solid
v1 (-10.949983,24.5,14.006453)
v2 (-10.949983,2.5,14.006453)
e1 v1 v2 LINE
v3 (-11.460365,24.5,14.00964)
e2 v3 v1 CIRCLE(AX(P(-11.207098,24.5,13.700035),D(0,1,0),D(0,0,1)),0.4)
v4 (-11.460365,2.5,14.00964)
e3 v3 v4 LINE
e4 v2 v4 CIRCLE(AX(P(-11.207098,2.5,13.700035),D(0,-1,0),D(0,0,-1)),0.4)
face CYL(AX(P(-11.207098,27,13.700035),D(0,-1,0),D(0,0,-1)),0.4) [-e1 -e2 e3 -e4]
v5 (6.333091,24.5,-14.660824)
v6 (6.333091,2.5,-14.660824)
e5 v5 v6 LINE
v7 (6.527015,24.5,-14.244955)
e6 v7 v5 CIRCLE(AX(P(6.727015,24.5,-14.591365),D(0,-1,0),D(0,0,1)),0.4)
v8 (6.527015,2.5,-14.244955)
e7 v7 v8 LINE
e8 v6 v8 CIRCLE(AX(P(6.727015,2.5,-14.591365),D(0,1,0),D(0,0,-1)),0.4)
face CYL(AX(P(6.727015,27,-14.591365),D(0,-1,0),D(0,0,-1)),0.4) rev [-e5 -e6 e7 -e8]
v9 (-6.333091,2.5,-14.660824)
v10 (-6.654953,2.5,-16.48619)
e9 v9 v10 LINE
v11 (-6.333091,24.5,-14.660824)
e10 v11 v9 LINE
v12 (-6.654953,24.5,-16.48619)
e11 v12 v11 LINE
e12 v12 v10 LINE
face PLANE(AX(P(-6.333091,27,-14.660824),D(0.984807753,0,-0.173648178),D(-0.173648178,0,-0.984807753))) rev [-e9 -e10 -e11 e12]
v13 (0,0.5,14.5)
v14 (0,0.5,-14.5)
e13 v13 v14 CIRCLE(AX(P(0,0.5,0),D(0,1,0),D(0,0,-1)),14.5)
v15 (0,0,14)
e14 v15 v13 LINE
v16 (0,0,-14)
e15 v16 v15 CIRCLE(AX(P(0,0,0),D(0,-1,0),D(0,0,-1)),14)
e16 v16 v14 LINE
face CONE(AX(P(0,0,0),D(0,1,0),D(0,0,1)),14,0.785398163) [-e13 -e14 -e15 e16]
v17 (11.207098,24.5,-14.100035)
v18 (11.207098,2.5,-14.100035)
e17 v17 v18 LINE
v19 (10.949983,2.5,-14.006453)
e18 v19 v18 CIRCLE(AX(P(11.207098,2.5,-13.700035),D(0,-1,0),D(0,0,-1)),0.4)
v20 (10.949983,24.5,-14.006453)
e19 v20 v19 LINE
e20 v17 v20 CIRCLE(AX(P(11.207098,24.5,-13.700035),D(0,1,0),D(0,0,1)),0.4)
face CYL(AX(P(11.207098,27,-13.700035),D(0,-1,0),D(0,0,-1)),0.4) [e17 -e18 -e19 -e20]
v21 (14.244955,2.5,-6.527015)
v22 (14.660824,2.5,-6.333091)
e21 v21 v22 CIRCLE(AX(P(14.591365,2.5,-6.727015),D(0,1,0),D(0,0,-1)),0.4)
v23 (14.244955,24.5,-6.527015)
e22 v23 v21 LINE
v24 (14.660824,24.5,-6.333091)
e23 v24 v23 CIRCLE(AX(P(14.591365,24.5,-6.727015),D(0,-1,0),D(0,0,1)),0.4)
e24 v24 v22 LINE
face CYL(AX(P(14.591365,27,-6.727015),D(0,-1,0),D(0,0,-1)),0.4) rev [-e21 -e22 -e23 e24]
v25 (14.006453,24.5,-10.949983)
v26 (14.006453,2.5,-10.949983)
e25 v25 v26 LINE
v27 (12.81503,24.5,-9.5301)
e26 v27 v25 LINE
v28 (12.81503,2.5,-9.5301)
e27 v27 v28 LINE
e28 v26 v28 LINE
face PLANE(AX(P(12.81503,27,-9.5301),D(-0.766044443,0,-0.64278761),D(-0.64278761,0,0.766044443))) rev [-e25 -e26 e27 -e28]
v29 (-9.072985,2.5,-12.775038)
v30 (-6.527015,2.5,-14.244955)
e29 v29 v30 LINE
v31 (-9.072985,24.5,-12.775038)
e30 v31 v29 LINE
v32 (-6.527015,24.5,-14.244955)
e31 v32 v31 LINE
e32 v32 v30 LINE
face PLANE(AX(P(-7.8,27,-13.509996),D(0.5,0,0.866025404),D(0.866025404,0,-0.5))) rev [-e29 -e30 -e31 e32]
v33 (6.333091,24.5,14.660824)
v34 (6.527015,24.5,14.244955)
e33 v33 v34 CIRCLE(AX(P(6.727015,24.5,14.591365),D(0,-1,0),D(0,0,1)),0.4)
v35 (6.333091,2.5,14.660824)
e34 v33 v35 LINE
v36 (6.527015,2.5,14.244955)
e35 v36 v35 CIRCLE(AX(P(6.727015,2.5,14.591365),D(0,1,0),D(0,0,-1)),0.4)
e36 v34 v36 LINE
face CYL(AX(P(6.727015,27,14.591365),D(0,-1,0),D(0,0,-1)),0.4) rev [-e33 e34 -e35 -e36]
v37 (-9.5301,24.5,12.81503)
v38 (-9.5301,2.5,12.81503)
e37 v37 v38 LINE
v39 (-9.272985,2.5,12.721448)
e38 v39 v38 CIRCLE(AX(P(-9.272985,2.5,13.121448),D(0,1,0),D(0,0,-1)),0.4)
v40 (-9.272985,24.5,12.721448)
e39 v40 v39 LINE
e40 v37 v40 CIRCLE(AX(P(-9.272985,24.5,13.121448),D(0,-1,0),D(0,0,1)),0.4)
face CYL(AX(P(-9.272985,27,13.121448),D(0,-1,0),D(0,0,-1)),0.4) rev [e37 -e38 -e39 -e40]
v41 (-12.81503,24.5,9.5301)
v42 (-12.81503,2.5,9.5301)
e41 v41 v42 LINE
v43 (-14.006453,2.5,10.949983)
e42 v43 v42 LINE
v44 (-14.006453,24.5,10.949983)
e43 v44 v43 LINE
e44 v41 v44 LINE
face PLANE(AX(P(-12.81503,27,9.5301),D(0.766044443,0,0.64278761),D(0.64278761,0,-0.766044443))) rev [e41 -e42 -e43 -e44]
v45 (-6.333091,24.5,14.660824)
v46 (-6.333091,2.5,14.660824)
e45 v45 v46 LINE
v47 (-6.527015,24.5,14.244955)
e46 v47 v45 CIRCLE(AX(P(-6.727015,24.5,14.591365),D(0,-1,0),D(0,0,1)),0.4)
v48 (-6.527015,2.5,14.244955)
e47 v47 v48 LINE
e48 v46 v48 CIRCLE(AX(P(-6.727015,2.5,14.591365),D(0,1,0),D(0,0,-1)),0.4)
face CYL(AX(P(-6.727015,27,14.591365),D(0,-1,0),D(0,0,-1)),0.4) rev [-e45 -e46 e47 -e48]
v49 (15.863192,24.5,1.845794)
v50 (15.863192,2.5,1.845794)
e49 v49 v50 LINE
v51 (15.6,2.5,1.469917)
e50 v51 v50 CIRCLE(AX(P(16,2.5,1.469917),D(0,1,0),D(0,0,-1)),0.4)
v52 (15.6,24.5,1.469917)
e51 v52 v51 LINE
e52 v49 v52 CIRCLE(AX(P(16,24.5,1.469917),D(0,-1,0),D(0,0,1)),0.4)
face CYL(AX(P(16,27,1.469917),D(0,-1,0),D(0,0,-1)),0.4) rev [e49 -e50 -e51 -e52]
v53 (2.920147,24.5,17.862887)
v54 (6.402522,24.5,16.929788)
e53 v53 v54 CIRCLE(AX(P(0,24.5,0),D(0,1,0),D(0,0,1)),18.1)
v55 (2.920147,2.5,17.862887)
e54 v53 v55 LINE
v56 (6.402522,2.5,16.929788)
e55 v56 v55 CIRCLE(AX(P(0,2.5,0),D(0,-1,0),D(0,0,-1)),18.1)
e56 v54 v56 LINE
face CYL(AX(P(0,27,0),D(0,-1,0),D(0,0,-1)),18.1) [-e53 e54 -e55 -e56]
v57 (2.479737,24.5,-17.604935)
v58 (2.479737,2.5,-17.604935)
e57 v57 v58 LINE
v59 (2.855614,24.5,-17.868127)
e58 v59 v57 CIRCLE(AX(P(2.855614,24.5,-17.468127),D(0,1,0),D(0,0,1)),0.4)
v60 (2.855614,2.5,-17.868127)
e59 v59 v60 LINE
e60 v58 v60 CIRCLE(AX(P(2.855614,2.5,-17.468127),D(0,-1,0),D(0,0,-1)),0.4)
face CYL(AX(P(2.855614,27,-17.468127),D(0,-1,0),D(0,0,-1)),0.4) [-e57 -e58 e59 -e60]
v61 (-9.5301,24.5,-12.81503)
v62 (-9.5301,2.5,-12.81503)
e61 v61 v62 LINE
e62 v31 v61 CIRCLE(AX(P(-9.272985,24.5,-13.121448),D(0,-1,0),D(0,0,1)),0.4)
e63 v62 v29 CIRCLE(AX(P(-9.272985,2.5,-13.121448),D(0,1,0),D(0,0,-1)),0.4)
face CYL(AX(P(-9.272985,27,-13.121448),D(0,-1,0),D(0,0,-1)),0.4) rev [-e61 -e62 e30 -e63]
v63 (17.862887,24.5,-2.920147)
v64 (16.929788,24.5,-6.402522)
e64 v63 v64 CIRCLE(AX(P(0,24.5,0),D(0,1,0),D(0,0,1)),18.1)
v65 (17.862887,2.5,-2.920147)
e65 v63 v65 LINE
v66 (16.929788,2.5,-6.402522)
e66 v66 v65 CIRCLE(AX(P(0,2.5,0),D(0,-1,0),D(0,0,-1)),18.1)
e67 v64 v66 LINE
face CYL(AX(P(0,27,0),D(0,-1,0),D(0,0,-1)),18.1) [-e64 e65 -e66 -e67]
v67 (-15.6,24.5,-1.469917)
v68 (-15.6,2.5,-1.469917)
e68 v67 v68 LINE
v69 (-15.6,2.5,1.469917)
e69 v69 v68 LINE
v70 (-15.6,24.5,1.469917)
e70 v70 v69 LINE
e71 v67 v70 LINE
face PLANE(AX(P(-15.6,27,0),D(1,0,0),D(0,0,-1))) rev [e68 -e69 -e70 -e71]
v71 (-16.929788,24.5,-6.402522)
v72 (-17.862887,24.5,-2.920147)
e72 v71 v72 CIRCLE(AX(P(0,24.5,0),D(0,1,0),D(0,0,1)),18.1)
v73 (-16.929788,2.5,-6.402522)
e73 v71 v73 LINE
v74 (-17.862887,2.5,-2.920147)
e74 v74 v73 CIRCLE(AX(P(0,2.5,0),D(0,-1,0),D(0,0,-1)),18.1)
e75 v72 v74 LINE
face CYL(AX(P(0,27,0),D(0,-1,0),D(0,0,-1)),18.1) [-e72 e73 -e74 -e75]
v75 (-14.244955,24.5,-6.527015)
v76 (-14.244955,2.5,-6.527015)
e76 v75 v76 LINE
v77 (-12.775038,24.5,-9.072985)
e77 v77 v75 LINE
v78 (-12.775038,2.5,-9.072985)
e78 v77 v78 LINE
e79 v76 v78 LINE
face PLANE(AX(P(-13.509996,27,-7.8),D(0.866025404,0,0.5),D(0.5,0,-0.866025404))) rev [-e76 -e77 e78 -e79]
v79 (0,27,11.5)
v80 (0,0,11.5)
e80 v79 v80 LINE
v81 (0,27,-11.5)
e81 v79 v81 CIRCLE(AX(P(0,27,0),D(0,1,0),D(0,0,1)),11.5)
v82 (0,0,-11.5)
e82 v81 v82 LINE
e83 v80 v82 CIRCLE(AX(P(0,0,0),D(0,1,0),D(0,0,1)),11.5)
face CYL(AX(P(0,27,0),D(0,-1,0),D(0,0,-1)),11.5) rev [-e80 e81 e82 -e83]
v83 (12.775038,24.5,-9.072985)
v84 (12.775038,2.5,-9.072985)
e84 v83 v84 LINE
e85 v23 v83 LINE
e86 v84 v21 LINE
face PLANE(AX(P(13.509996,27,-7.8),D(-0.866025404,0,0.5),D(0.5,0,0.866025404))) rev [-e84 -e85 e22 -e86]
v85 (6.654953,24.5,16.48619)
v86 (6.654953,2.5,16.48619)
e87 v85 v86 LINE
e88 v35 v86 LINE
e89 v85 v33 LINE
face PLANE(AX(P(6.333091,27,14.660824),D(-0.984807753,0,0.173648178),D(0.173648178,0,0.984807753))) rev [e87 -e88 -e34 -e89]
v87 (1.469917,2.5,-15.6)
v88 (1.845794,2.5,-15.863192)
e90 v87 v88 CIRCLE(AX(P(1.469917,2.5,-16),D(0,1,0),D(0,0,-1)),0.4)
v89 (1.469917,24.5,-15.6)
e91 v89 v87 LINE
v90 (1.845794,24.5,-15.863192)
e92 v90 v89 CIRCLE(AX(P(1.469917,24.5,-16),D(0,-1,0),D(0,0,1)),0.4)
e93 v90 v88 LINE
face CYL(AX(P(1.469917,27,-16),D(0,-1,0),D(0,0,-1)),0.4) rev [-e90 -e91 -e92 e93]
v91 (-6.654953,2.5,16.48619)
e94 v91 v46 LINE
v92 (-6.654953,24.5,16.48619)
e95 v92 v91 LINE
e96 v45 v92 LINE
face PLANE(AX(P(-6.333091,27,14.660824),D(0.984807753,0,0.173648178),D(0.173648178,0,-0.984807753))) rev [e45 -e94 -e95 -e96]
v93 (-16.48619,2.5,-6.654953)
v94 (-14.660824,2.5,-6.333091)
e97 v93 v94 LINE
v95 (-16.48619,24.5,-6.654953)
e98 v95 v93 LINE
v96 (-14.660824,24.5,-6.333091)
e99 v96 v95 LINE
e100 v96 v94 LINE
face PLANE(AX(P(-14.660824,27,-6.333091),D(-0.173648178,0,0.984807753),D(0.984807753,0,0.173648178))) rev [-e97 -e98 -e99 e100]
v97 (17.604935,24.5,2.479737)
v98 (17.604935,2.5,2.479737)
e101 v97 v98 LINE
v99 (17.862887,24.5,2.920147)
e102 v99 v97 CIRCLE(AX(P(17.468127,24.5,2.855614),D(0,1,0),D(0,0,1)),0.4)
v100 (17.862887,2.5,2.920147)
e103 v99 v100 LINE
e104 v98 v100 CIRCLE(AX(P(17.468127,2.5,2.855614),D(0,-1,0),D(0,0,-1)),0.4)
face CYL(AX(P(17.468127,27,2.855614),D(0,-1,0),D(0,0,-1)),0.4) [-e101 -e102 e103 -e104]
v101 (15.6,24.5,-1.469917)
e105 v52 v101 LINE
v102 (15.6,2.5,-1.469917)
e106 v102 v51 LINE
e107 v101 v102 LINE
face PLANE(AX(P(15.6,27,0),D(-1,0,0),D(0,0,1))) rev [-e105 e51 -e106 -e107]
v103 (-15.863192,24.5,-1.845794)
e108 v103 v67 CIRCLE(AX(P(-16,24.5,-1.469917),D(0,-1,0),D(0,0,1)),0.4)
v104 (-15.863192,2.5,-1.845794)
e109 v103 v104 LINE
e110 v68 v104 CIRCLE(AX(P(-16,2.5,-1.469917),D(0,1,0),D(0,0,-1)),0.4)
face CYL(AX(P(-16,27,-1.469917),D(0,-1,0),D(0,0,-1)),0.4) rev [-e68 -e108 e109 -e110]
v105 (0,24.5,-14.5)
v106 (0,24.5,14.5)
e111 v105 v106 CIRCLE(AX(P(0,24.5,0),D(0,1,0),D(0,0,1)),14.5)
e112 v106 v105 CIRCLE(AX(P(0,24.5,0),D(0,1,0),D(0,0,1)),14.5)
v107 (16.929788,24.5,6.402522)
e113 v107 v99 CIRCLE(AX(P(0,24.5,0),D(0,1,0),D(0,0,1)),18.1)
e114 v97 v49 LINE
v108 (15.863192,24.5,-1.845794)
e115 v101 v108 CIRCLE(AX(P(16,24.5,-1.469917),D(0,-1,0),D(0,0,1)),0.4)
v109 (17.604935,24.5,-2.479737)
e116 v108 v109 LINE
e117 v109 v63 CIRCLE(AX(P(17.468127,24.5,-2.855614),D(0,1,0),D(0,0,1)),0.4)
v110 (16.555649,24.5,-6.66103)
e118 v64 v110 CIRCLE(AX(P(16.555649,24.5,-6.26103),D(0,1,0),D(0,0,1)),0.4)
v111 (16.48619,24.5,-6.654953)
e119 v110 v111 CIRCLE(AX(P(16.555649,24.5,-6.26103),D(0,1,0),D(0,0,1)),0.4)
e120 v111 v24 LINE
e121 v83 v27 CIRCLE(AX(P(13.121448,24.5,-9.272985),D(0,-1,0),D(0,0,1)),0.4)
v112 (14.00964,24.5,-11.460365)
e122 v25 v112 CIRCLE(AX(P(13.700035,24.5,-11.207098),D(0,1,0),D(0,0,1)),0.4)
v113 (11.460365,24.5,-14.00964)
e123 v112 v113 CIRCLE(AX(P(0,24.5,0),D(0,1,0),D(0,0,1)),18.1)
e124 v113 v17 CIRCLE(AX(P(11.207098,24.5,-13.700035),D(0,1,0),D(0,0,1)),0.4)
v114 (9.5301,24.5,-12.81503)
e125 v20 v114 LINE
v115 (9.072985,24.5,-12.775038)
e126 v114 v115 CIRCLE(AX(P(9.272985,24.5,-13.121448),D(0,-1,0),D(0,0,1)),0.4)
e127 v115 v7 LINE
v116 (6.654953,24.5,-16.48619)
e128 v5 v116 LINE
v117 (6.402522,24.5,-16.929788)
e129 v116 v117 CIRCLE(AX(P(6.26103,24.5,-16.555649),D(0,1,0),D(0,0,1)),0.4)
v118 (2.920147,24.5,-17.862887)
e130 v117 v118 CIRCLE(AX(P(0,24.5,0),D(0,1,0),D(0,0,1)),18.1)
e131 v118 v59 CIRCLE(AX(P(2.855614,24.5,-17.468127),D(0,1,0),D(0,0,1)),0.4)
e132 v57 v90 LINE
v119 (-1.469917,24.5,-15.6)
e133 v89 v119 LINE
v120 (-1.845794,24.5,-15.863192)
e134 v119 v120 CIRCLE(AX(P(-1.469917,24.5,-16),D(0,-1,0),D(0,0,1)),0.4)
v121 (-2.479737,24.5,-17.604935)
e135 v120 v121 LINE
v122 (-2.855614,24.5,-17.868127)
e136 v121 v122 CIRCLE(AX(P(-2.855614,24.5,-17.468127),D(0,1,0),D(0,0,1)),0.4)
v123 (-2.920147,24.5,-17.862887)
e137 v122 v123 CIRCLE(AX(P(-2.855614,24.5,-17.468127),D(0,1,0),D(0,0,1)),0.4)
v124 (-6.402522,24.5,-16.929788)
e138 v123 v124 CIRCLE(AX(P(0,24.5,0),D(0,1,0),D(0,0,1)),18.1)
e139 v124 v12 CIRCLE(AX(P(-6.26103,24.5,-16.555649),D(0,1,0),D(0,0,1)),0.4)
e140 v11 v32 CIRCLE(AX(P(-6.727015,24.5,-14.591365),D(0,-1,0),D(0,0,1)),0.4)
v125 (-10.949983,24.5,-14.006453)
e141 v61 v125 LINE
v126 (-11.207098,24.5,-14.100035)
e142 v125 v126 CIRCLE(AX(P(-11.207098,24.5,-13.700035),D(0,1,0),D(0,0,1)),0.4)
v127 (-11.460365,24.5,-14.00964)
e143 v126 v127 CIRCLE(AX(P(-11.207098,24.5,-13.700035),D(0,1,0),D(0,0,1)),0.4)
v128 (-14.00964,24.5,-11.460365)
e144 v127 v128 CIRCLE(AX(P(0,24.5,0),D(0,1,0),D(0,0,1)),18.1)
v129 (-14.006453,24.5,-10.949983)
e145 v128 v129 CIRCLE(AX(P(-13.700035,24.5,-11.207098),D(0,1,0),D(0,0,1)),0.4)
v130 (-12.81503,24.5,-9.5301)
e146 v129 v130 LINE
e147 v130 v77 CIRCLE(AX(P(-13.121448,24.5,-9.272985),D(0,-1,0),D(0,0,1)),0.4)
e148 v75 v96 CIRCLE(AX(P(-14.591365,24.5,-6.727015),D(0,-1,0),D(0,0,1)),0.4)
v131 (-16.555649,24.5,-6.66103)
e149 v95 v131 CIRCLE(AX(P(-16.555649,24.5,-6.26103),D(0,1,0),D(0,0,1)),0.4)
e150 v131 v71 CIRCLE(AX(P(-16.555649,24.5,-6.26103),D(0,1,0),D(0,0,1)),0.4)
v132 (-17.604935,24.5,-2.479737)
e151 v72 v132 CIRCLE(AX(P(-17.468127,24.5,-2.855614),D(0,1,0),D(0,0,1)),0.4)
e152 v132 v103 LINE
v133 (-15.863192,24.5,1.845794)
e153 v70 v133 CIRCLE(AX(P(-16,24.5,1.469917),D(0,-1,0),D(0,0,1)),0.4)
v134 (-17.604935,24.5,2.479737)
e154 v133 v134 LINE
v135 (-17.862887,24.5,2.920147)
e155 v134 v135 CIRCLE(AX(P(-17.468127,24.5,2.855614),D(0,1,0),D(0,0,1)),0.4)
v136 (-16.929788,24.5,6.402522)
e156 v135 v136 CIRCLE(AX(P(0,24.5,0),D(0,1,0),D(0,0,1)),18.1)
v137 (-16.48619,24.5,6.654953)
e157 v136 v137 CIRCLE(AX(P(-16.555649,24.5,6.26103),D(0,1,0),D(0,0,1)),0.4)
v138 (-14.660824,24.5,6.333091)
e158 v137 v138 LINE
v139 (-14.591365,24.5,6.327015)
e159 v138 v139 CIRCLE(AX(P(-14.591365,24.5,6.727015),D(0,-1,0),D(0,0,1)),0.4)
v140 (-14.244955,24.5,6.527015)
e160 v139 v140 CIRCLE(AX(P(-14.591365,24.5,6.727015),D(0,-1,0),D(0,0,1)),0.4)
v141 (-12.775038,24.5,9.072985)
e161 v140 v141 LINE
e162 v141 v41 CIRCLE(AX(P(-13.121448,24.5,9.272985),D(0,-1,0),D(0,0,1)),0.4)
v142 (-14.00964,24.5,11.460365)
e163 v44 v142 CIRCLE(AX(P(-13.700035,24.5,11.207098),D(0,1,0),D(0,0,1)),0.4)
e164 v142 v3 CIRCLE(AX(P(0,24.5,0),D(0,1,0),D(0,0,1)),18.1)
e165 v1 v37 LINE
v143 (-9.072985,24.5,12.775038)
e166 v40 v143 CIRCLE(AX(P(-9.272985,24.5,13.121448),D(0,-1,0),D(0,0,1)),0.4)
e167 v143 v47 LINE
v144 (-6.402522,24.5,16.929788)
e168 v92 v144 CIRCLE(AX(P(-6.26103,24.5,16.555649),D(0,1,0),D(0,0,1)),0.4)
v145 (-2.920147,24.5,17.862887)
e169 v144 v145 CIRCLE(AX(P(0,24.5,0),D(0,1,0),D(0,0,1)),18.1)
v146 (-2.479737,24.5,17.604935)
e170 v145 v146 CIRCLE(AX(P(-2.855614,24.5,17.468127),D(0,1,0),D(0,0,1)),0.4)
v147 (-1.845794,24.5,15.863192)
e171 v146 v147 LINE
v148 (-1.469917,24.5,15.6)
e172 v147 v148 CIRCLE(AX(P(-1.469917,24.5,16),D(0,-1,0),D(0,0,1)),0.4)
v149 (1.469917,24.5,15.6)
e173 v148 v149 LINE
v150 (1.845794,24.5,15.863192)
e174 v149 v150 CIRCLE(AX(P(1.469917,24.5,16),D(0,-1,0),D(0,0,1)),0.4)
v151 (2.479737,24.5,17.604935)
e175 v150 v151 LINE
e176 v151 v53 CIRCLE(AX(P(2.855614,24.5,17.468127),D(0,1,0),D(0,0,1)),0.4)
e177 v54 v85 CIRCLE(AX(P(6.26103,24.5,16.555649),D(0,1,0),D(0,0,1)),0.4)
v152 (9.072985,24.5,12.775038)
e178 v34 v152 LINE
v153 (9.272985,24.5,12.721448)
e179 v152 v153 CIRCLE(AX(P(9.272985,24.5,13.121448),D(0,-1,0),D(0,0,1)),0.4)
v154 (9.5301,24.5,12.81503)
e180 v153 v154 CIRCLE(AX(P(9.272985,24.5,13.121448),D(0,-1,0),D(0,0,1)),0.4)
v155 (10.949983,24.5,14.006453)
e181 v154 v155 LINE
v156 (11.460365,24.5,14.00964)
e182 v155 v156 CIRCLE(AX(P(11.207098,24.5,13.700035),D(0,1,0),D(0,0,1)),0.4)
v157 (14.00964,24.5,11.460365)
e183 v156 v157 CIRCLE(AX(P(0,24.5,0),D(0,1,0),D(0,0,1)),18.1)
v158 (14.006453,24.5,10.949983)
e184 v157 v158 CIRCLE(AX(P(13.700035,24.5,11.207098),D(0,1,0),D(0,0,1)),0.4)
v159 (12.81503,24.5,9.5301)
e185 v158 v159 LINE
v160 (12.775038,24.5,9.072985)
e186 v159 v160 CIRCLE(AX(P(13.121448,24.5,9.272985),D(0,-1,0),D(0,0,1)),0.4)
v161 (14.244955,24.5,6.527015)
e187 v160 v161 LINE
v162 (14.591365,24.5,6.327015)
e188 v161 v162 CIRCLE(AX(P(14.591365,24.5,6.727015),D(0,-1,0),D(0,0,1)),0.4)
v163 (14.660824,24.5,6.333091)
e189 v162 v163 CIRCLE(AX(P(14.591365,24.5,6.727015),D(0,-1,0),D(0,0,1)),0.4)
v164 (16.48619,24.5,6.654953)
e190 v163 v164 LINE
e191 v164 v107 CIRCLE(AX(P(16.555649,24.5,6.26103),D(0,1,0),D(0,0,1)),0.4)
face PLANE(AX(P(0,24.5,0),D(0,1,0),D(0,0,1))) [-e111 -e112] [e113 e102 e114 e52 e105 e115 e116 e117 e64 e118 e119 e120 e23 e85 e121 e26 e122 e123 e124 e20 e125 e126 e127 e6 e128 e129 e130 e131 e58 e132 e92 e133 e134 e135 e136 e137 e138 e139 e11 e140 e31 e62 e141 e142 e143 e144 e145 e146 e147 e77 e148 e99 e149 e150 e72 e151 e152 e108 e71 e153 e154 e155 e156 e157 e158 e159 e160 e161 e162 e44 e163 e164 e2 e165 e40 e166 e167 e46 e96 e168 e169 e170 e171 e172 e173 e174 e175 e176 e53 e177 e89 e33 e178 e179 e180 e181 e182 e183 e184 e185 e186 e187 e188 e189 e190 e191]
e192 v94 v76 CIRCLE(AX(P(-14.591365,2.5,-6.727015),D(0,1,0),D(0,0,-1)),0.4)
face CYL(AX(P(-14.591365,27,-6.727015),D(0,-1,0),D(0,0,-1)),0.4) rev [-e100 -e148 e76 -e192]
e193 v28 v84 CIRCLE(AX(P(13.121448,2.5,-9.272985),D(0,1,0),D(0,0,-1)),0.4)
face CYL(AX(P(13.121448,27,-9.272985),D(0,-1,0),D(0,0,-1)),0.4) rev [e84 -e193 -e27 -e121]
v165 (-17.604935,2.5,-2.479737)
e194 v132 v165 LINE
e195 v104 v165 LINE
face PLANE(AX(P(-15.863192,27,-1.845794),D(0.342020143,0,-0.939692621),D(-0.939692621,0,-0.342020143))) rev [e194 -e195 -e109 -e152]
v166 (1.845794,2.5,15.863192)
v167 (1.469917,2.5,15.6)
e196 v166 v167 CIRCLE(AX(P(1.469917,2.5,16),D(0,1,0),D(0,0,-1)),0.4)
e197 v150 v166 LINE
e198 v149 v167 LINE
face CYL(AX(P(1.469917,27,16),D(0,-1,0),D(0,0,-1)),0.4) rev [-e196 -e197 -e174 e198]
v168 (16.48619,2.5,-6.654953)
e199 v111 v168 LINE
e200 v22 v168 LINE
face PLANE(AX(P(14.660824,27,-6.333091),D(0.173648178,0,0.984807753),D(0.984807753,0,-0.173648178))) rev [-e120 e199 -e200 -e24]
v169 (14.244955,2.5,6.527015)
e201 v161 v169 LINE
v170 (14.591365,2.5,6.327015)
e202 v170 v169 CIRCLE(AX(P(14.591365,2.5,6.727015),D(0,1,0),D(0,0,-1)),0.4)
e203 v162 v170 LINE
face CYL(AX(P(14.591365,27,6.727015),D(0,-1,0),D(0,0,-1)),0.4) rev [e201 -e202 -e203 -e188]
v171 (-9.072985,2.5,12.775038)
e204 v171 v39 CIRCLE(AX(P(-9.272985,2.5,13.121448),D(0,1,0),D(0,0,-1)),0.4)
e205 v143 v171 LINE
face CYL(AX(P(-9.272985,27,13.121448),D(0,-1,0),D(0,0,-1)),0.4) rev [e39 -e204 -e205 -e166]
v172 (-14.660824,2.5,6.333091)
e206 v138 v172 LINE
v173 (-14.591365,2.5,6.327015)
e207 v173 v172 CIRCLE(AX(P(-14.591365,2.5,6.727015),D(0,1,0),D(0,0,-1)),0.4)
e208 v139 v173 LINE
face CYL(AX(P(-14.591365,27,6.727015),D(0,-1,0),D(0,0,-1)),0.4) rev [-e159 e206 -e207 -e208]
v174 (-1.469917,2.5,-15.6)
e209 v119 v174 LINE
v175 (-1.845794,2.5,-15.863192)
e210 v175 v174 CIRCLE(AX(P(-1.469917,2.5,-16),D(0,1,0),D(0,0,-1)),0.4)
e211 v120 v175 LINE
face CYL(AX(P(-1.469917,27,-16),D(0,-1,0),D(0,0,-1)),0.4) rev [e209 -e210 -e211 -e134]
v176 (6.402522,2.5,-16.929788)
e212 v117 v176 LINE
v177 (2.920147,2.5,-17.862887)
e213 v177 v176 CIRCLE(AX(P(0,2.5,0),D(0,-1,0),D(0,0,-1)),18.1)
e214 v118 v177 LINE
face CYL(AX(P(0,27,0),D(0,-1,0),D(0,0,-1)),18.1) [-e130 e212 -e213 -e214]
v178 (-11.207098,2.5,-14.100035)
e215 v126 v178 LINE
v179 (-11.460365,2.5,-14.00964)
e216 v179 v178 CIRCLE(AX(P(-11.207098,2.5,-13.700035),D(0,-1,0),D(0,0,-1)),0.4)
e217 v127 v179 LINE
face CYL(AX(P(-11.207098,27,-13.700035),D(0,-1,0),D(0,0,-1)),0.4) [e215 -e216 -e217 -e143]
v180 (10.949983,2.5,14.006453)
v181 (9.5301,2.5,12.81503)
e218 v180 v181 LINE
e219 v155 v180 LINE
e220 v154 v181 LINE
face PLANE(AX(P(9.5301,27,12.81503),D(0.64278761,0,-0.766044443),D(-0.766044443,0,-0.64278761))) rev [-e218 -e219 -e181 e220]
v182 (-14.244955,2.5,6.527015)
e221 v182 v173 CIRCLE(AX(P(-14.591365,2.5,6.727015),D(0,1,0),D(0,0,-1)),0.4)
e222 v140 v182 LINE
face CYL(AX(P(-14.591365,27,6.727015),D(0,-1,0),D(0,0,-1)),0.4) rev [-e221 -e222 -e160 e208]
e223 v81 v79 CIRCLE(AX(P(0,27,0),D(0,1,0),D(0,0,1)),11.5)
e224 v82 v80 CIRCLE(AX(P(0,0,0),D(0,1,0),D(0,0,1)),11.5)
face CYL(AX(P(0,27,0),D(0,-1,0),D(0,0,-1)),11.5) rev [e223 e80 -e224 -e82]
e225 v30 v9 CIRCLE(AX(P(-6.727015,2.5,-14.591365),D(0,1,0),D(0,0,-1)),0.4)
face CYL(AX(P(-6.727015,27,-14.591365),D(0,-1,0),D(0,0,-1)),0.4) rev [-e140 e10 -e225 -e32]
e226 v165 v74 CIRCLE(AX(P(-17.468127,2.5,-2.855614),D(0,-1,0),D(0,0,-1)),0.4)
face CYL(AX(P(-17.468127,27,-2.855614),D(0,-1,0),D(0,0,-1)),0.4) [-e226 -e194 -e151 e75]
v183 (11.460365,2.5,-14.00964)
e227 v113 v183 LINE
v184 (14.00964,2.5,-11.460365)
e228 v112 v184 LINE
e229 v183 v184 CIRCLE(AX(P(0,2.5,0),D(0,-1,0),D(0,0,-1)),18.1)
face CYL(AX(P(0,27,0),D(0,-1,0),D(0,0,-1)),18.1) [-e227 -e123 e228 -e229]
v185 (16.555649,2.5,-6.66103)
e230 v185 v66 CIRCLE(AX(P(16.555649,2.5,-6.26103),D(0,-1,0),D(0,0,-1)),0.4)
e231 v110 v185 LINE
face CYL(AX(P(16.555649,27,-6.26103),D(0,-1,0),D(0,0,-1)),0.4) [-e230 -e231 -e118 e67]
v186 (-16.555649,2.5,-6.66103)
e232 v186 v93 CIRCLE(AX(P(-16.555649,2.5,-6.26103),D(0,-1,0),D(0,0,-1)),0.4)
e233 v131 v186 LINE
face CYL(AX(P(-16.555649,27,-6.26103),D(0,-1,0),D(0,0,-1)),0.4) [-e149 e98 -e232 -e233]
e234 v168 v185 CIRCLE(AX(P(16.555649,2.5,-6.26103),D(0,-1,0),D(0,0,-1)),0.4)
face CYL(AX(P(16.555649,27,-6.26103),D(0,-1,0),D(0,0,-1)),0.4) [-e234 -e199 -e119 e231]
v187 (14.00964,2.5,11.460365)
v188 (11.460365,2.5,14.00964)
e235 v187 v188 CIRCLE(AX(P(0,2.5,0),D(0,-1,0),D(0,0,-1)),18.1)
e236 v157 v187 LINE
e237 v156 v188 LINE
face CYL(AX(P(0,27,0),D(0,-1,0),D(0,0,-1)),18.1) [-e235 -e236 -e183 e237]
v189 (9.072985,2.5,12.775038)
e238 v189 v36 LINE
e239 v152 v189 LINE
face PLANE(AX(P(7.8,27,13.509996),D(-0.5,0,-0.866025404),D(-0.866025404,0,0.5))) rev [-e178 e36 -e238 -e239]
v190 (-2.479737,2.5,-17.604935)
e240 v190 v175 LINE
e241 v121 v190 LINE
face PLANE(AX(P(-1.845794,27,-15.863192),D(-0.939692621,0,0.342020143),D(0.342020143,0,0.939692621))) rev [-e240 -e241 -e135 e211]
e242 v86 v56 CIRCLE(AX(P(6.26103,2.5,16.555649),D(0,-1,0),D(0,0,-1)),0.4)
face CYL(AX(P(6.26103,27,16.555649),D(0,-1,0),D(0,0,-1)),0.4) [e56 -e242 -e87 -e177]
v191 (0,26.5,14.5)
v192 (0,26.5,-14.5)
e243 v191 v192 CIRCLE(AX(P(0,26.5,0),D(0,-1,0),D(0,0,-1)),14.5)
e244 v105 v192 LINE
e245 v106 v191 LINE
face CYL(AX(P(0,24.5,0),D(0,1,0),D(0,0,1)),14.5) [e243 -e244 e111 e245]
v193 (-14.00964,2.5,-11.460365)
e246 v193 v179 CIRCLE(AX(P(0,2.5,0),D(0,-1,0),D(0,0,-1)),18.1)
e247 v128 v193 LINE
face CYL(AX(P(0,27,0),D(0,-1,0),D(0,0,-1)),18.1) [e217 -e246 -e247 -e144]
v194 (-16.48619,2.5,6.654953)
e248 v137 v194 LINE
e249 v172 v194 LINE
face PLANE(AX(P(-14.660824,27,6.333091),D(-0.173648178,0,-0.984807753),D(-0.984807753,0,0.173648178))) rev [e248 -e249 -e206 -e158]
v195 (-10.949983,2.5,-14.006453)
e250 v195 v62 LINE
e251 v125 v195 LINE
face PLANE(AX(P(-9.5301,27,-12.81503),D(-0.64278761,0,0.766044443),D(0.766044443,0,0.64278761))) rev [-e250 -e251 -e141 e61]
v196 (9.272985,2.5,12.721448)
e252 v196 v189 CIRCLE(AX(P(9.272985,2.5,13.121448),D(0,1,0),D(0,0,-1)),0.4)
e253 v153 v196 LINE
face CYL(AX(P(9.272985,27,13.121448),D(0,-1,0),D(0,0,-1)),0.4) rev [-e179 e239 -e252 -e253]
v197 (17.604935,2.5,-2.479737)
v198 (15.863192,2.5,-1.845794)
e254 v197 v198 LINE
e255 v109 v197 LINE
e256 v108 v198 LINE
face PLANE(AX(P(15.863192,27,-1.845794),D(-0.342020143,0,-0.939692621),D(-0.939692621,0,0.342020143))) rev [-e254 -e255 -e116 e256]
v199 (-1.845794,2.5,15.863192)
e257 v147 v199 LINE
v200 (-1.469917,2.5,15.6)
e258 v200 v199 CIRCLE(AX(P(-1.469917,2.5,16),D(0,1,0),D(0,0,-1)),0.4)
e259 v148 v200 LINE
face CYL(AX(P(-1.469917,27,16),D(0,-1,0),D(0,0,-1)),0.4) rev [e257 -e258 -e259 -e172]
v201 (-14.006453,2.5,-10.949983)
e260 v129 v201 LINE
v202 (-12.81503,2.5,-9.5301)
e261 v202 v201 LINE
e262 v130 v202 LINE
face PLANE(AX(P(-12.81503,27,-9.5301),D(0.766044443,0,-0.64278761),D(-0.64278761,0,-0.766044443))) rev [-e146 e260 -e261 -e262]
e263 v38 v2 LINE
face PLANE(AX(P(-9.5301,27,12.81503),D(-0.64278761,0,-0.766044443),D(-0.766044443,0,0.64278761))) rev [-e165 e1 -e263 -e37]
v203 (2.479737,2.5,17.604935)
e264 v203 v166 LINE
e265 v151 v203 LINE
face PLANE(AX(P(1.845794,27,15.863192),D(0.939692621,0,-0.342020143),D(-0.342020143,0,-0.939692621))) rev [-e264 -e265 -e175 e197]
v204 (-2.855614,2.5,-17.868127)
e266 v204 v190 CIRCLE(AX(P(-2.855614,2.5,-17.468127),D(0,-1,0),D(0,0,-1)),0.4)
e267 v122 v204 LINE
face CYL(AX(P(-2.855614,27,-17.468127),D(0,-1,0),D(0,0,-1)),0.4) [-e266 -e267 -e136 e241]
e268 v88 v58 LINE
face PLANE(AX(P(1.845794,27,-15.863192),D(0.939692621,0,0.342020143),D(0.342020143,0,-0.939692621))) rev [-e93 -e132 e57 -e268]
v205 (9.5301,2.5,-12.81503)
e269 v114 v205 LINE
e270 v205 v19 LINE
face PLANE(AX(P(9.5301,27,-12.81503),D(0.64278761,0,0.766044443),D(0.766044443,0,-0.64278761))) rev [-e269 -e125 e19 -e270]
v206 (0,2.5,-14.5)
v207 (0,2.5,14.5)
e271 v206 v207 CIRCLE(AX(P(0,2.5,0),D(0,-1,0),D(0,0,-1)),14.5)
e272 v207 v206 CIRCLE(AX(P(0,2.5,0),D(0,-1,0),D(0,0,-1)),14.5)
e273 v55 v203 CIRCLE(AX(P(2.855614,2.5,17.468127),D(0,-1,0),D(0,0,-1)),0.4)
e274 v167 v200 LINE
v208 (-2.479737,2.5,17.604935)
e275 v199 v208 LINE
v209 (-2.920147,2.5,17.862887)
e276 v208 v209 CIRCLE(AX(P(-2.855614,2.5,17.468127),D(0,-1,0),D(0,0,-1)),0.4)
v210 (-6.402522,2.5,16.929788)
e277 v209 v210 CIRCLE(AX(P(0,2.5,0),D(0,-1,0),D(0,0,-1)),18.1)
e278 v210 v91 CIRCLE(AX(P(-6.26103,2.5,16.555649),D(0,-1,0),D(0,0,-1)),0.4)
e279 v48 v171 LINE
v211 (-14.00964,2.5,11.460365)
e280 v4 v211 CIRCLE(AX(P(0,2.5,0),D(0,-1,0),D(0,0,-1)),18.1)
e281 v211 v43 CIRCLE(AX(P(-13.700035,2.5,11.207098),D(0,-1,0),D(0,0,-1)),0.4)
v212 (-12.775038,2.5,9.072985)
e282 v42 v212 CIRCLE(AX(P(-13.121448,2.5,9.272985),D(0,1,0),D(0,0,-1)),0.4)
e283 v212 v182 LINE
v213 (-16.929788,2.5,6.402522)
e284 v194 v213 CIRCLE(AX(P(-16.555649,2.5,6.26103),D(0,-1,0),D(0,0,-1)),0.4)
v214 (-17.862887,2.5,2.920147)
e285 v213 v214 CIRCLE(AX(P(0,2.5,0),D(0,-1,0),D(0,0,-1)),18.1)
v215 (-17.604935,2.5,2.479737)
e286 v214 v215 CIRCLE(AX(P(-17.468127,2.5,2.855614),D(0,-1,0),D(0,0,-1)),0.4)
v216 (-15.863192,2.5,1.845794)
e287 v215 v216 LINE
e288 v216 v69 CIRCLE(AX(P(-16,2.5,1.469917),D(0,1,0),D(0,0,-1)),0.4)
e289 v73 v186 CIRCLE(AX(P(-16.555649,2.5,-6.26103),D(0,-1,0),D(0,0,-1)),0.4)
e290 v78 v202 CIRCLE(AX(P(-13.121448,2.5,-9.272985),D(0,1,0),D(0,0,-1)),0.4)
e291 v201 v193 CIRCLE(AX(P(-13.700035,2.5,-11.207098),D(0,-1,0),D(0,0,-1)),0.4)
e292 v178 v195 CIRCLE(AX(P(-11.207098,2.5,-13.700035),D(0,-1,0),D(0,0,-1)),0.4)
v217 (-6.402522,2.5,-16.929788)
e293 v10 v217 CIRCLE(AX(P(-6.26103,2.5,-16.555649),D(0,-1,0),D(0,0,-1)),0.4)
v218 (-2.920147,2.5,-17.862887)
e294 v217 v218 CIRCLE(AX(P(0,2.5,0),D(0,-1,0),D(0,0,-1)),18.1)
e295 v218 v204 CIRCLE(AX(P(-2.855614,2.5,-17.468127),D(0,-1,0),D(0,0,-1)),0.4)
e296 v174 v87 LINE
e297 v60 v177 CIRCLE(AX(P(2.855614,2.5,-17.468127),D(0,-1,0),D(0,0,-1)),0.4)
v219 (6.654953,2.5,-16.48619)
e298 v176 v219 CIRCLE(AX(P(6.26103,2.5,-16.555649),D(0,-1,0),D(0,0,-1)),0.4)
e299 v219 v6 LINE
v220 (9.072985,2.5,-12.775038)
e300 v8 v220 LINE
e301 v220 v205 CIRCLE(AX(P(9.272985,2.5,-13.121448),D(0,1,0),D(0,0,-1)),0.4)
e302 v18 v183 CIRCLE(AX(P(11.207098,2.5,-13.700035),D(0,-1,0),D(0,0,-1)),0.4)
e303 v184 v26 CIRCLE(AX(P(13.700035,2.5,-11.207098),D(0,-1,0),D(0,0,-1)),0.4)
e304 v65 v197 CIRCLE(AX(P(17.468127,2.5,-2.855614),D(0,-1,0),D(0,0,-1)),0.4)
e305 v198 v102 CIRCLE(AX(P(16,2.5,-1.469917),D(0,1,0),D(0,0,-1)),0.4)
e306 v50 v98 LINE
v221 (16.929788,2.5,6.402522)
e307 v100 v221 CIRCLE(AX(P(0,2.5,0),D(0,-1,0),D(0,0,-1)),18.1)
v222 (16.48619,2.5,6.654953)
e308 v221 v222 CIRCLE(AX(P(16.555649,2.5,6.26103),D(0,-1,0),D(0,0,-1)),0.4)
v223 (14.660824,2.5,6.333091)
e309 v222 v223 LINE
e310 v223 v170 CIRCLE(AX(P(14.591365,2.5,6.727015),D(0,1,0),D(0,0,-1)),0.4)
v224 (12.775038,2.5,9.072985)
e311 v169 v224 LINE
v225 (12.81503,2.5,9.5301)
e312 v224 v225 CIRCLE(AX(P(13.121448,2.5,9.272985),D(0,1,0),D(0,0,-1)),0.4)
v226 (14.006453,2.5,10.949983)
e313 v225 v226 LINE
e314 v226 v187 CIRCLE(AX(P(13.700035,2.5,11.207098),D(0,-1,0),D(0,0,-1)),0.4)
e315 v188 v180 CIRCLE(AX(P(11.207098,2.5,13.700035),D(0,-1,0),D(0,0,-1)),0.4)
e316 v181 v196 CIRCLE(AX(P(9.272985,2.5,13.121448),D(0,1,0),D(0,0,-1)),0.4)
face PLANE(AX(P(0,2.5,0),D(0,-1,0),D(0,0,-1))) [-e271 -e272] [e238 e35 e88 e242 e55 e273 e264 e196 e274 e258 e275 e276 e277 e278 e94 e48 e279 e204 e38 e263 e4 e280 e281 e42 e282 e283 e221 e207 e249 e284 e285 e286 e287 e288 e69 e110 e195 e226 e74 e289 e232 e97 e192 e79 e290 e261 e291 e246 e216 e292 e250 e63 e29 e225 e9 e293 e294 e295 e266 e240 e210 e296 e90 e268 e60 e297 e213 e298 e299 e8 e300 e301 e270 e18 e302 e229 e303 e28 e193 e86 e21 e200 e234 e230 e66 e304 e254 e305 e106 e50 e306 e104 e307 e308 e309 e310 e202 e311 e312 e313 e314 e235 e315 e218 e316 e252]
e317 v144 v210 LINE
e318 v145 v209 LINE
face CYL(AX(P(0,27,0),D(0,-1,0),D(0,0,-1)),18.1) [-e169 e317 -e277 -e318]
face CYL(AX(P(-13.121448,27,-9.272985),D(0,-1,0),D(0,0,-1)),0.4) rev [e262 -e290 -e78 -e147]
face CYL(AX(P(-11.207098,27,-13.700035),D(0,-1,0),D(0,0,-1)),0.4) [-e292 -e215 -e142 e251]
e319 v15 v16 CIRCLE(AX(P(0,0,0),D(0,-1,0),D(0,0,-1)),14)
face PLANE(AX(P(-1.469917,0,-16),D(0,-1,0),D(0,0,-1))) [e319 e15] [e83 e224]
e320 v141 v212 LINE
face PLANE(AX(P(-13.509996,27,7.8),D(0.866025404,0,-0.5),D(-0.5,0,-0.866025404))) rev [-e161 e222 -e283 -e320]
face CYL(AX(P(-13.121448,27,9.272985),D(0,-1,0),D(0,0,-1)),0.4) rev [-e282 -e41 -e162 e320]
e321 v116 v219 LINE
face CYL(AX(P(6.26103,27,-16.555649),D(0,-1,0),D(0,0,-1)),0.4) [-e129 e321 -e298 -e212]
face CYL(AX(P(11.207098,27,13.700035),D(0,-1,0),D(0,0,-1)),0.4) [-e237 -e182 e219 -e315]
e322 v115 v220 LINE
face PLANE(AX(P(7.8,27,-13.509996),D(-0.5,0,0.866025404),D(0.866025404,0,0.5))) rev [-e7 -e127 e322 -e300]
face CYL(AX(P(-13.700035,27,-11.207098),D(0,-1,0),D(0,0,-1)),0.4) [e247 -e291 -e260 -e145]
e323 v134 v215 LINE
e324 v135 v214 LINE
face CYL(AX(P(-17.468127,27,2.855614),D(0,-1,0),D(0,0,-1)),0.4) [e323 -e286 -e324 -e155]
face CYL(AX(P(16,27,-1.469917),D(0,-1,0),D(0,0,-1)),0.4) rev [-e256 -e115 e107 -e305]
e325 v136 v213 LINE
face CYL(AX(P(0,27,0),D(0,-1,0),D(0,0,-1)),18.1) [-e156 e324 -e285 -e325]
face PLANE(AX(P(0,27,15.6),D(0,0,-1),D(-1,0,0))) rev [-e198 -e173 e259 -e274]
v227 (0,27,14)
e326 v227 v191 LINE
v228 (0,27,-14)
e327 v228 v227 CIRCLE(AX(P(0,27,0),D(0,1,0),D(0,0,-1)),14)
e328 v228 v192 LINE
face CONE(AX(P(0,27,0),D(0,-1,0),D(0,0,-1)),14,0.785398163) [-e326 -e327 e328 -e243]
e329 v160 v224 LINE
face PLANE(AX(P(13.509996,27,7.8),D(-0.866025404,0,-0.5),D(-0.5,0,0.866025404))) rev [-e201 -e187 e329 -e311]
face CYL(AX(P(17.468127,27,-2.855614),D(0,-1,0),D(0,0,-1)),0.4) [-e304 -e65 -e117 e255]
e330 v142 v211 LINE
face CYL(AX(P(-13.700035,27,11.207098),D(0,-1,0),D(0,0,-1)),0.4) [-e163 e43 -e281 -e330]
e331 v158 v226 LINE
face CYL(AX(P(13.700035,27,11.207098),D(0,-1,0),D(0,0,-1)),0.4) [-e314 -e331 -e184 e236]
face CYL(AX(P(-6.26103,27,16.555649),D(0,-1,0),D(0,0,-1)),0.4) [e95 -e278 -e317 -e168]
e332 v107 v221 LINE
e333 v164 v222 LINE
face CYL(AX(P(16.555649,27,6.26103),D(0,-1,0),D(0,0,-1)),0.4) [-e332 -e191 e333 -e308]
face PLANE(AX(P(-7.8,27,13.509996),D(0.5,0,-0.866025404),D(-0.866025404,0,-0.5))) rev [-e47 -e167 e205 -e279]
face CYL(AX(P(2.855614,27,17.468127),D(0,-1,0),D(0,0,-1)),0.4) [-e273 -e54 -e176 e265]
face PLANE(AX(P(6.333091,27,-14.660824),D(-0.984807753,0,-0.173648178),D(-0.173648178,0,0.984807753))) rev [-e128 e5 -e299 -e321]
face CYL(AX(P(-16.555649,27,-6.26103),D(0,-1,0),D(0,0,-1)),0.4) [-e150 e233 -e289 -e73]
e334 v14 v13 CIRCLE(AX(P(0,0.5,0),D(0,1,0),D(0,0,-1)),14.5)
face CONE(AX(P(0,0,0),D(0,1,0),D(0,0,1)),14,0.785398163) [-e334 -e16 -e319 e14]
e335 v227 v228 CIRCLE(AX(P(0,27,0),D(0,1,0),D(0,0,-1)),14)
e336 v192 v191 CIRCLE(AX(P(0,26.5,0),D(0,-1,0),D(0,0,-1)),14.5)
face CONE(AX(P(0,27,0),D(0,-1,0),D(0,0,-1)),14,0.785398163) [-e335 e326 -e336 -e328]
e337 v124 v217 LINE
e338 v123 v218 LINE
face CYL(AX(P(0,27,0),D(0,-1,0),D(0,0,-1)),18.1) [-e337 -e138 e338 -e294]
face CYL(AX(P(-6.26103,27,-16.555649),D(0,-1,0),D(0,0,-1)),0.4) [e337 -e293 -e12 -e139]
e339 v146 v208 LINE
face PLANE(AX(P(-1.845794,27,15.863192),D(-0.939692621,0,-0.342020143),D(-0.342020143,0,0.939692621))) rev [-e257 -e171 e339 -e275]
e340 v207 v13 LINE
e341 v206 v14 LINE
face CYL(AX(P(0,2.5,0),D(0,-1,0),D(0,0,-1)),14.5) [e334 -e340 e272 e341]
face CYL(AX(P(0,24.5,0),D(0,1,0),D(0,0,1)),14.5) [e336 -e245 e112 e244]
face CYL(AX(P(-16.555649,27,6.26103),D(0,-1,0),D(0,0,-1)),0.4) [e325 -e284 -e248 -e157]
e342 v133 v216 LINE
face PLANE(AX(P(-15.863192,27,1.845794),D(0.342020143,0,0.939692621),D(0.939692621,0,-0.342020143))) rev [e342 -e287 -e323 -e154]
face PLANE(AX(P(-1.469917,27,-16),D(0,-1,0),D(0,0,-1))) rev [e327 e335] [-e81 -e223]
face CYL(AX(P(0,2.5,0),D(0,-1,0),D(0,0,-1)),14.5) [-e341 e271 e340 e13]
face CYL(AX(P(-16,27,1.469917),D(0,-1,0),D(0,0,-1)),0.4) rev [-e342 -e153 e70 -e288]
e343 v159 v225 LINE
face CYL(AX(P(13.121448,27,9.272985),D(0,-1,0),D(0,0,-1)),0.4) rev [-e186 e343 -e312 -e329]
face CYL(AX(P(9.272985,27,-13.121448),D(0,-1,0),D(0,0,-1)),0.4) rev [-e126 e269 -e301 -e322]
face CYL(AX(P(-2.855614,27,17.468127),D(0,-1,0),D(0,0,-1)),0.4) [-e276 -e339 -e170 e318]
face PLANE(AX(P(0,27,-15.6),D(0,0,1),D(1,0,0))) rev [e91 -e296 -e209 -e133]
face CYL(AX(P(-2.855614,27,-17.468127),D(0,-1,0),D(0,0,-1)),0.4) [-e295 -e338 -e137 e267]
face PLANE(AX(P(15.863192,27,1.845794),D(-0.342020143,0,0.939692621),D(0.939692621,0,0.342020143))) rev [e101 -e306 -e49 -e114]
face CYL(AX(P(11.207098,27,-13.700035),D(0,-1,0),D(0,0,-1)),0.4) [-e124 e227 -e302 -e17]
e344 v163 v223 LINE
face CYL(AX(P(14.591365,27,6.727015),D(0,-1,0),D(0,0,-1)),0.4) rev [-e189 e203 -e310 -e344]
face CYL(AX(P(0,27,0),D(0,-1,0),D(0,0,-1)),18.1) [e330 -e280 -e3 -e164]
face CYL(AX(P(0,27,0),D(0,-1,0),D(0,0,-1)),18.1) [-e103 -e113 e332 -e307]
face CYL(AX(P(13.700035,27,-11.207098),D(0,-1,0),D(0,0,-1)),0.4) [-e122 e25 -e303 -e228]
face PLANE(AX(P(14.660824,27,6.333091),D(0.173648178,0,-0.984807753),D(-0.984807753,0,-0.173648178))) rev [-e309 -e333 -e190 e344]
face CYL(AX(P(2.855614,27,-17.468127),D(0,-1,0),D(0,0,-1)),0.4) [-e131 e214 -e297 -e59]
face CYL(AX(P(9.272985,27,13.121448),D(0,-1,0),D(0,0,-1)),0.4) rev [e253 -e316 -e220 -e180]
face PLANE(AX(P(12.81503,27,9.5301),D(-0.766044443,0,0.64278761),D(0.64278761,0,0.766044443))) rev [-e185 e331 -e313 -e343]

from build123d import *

# Parameters (mm, degrees)
SKETCH_1_R          = 11.5
EXTRUDE_1_DEPTH     = 27
CUT_EXTRUDE_START   = -2.5
SKETCH_2_R          = 18.1
SKETCH_2_R_2        = 14.5
CUT_EXTRUDE_1_DEPTH = 2.5
SKETCH_3_R          = 18.1
SKETCH_3_R_2        = 14.5
CUT_EXTRUDE_2_DEPTH = 2.5
CHAMFER_1_SIZE      = 0.5


with BuildPart() as part:
    # 草图1 → 拉伸1 (new body)
    with BuildSketch(Plane(origin=(0, 0, 0), x_dir=(1, 0, 0), z_dir=(0, 1, 0))):
        with BuildLine():
            Line((7.8, 13.509996299), (9.07298545, 12.775037807))
            ThreePointArc((9.07298545, 12.775037807), (9.307847747, 12.722970089), (9.530100494, 12.815030191))
            Line((9.530100494, 12.815030191), (10.949982696, 14.006452823))
            ThreePointArc((10.949982696, 14.006452823), (11.204599636, 14.100027245), (11.460365485, 14.009640357))
            ThreePointArc((11.460365485, 14.009640357), (12.798632739, 12.798632739), (14.009640357, 11.460365485))
            ThreePointArc((14.009640357, 11.460365485), (14.100027245, 11.204599636), (14.006452823, 10.949982696))
            Line((14.006452823, 10.949982696), (12.815030191, 9.530100494))
            ThreePointArc((12.815030191, 9.530100494), (12.722970089, 9.307847747), (12.775037807, 9.07298545))
            Line((12.775037807, 9.07298545), (13.509996299, 7.8))
            Line((13.509996299, 7.8), (14.244954791, 6.52701455))
            ThreePointArc((14.244954791, 6.52701455), (14.422317648, 6.364491435), (14.660824224, 6.333091449))
            Line((14.660824224, 6.333091449), (16.486189597, 6.654952614))
            ThreePointArc((16.486189597, 6.654952614), (16.753481547, 6.60868197), (16.929787826, 6.402521705))
            ThreePointArc((16.929787826, 6.402521705), (17.483257456, 4.684624716), (17.86288719, 2.920147468))
            ThreePointArc((17.86288719, 2.920147468), (17.813281606, 2.653454302), (17.604935309, 2.479736774))
            Line((17.604935309, 2.479736774), (15.863191943, 1.845794033))
            ThreePointArc((15.863191943, 1.845794033), (15.672339182, 1.699347559), (15.6, 1.469916985))
            Line((15.6, 1.469916985), (15.6, 0))
            Line((15.6, 0), (15.6, -1.469916985))
            ThreePointArc((15.6, -1.469916985), (15.672339182, -1.699347559), (15.863191943, -1.845794033))
            Line((15.863191943, -1.845794033), (17.604935309, -2.479736774))
            ThreePointArc((17.604935309, -2.479736774), (17.813281606, -2.653454302), (17.86288719, -2.920147468))
            ThreePointArc((17.86288719, -2.920147468), (17.483257456, -4.684624716), (16.929787826, -6.402521705))
            ThreePointArc((16.929787826, -6.402521705), (16.753481547, -6.60868197), (16.486189597, -6.654952614))
            Line((16.486189597, -6.654952614), (14.660824224, -6.333091449))
            ThreePointArc((14.660824224, -6.333091449), (14.422317648, -6.364491435), (14.244954791, -6.52701455))
            Line((14.244954791, -6.52701455), (13.509996299, -7.8))
            Line((13.509996299, -7.8), (12.775037807, -9.07298545))
            ThreePointArc((12.775037807, -9.07298545), (12.722970089, -9.307847747), (12.815030191, -9.530100494))
            Line((12.815030191, -9.530100494), (14.006452823, -10.949982696))
            ThreePointArc((14.006452823, -10.949982696), (14.100027245, -11.204599636), (14.009640357, -11.460365485))
            ThreePointArc((14.009640357, -11.460365485), (12.798632739, -12.798632739), (11.460365485, -14.009640357))
            ThreePointArc((11.460365485, -14.009640357), (11.204599636, -14.100027245), (10.949982696, -14.006452823))
            Line((10.949982696, -14.006452823), (9.530100494, -12.815030191))
            ThreePointArc((9.530100494, -12.815030191), (9.307847747, -12.722970089), (9.07298545, -12.775037807))
            Line((9.07298545, -12.775037807), (7.8, -13.509996299))
            Line((7.8, -13.509996299), (6.52701455, -14.244954791))
            ThreePointArc((6.52701455, -14.244954791), (6.364491435, -14.422317648), (6.333091449, -14.660824224))
            Line((6.333091449, -14.660824224), (6.654952614, -16.486189597))
            ThreePointArc((6.654952614, -16.486189597), (6.60868197, -16.753481547), (6.402521705, -16.929787826))
            ThreePointArc((6.402521705, -16.929787826), (4.684624716, -17.483257456), (2.920147468, -17.86288719))
            ThreePointArc((2.920147468, -17.86288719), (2.653454302, -17.813281606), (2.479736774, -17.604935309))
            Line((2.479736774, -17.604935309), (1.845794033, -15.863191943))
            ThreePointArc((1.845794033, -15.863191943), (1.699347559, -15.672339182), (1.469916985, -15.6))
            Line((1.469916985, -15.6), (0, -15.6))
            Line((0, -15.6), (-1.469916985, -15.6))
            ThreePointArc((-1.469916985, -15.6), (-1.699347559, -15.672339182), (-1.845794033, -15.863191943))
            Line((-1.845794033, -15.863191943), (-2.479736774, -17.604935309))
            ThreePointArc((-2.479736774, -17.604935309), (-2.653454302, -17.813281606), (-2.920147468, -17.86288719))
            ThreePointArc((-2.920147468, -17.86288719), (-4.684624716, -17.483257456), (-6.402521705, -16.929787826))
            ThreePointArc((-6.402521705, -16.929787826), (-6.60868197, -16.753481547), (-6.654952614, -16.486189597))
            Line((-6.654952614, -16.486189597), (-6.333091449, -14.660824224))
            ThreePointArc((-6.333091449, -14.660824224), (-6.364491435, -14.422317648), (-6.52701455, -14.244954791))
            Line((-6.52701455, -14.244954791), (-7.8, -13.509996299))
            Line((-7.8, -13.509996299), (-9.07298545, -12.775037807))
            ThreePointArc((-9.07298545, -12.775037807), (-9.307847747, -12.722970089), (-9.530100494, -12.815030191))
            Line((-9.530100494, -12.815030191), (-10.949982696, -14.006452823))
            ThreePointArc((-10.949982696, -14.006452823), (-11.204599636, -14.100027245), (-11.460365485, -14.009640357))
            ThreePointArc((-11.460365485, -14.009640357), (-12.798632739, -12.798632739), (-14.009640357, -11.460365485))
            ThreePointArc((-14.009640357, -11.460365485), (-14.100027245, -11.204599636), (-14.006452823, -10.949982696))
            Line((-14.006452823, -10.949982696), (-12.815030191, -9.530100494))
            ThreePointArc((-12.815030191, -9.530100494), (-12.722970089, -9.307847747), (-12.775037807, -9.07298545))
            Line((-12.775037807, -9.07298545), (-13.509996299, -7.8))
            Line((-13.509996299, -7.8), (-14.244954791, -6.52701455))
            ThreePointArc((-14.244954791, -6.52701455), (-14.422317648, -6.364491435), (-14.660824224, -6.333091449))
            Line((-14.660824224, -6.333091449), (-16.486189597, -6.654952614))
            ThreePointArc((-16.486189597, -6.654952614), (-16.753481547, -6.60868197), (-16.929787826, -6.402521705))
            ThreePointArc((-16.929787826, -6.402521705), (-17.483257456, -4.684624716), (-17.86288719, -2.920147468))
            ThreePointArc((-17.86288719, -2.920147468), (-17.813281606, -2.653454302), (-17.604935309, -2.479736774))
            Line((-17.604935309, -2.479736774), (-15.863191943, -1.845794033))
            ThreePointArc((-15.863191943, -1.845794033), (-15.672339182, -1.699347559), (-15.6, -1.469916985))
            Line((-15.6, -1.469916985), (-15.6, 0))
            Line((-15.6, 0), (-15.6, 1.469916985))
            ThreePointArc((-15.6, 1.469916985), (-15.672339182, 1.699347559), (-15.863191943, 1.845794033))
            Line((-15.863191943, 1.845794033), (-17.604935309, 2.479736774))
            ThreePointArc((-17.604935309, 2.479736774), (-17.813281606, 2.653454302), (-17.86288719, 2.920147468))
            ThreePointArc((-17.86288719, 2.920147468), (-17.483257456, 4.684624716), (-16.929787826, 6.402521705))
            ThreePointArc((-16.929787826, 6.402521705), (-16.753481547, 6.60868197), (-16.486189597, 6.654952614))
            Line((-16.486189597, 6.654952614), (-14.660824224, 6.333091449))
            ThreePointArc((-14.660824224, 6.333091449), (-14.422317648, 6.364491435), (-14.244954791, 6.52701455))
            Line((-14.244954791, 6.52701455), (-13.509996299, 7.8))
            Line((-13.509996299, 7.8), (-12.775037807, 9.07298545))
            ThreePointArc((-12.775037807, 9.07298545), (-12.722970089, 9.307847747), (-12.815030191, 9.530100494))
            Line((-12.815030191, 9.530100494), (-14.006452823, 10.949982696))
            ThreePointArc((-14.006452823, 10.949982696), (-14.100027245, 11.204599636), (-14.009640357, 11.460365485))
            ThreePointArc((-14.009640357, 11.460365485), (-12.798632739, 12.798632739), (-11.460365485, 14.009640357))
            ThreePointArc((-11.460365485, 14.009640357), (-11.204599636, 14.100027245), (-10.949982696, 14.006452823))
            Line((-10.949982696, 14.006452823), (-9.530100494, 12.815030191))
            ThreePointArc((-9.530100494, 12.815030191), (-9.307847747, 12.722970089), (-9.07298545, 12.775037807))
            Line((-9.07298545, 12.775037807), (-7.8, 13.509996299))
            Line((-7.8, 13.509996299), (-6.52701455, 14.244954791))
            ThreePointArc((-6.52701455, 14.244954791), (-6.364491435, 14.422317648), (-6.333091449, 14.660824224))
            Line((-6.333091449, 14.660824224), (-6.654952614, 16.486189597))
            ThreePointArc((-6.654952614, 16.486189597), (-6.60868197, 16.753481547), (-6.402521705, 16.929787826))
            ThreePointArc((-6.402521705, 16.929787826), (-4.684624716, 17.483257456), (-2.920147468, 17.86288719))
            ThreePointArc((-2.920147468, 17.86288719), (-2.653454302, 17.813281606), (-2.479736774, 17.604935309))
            Line((-2.479736774, 17.604935309), (-1.845794033, 15.863191943))
            ThreePointArc((-1.845794033, 15.863191943), (-1.699347559, 15.672339182), (-1.469916985, 15.6))
            Line((-1.469916985, 15.6), (0, 15.6))
            Line((0, 15.6), (1.469916985, 15.6))
            ThreePointArc((1.469916985, 15.6), (1.699347559, 15.672339182), (1.845794033, 15.863191943))
            Line((1.845794033, 15.863191943), (2.479736774, 17.604935309))
            ThreePointArc((2.479736774, 17.604935309), (2.653454302, 17.813281606), (2.920147468, 17.86288719))
            ThreePointArc((2.920147468, 17.86288719), (4.684624716, 17.483257456), (6.402521705, 16.929787826))
            ThreePointArc((6.402521705, 16.929787826), (6.60868197, 16.753481547), (6.654952614, 16.486189597))
            Line((6.654952614, 16.486189597), (6.333091449, 14.660824224))
            ThreePointArc((6.333091449, 14.660824224), (6.364491435, 14.422317648), (6.52701455, 14.244954791))
            Line((6.52701455, 14.244954791), (7.8, 13.509996299))
        make_face()
        with Locations(Location((0, 0, 0), (0, 0, 270))):
            Circle(SKETCH_1_R, mode=Mode.SUBTRACT)
    extrude(amount=EXTRUDE_1_DEPTH)

    # 草图2 → 切除-拉伸1 (cut)
    with BuildSketch(Plane(origin=(0, 27, 0), x_dir=(-1, 0, 0), z_dir=(0, 1, 0)).offset(CUT_EXTRUDE_START)):
        Circle(SKETCH_2_R)
        with Locations(Location((0, 0, 0), (0, 0, 90))):
            Circle(SKETCH_2_R_2, mode=Mode.SUBTRACT)
    extrude(amount=CUT_EXTRUDE_1_DEPTH, mode=Mode.SUBTRACT)

    # 草图3 → 切除-拉伸2 (cut)
    with BuildSketch(Plane.XZ):
        Circle(SKETCH_3_R)
        with Locations(Location((0, 0, 0), (0, 0, 90))):
            Circle(SKETCH_3_R_2, mode=Mode.SUBTRACT)
    extrude(amount=-CUT_EXTRUDE_2_DEPTH, mode=Mode.SUBTRACT)

    # 倒角1
    chamfer_1_edges = [part.edges().sort_by_distance(p)[0] for p in [
        (0, 27, -14.5),
        (0, 0, -14.5),
    ]]
    chamfer(chamfer_1_edges, length=CHAMFER_1_SIZE)


solid = part.part
